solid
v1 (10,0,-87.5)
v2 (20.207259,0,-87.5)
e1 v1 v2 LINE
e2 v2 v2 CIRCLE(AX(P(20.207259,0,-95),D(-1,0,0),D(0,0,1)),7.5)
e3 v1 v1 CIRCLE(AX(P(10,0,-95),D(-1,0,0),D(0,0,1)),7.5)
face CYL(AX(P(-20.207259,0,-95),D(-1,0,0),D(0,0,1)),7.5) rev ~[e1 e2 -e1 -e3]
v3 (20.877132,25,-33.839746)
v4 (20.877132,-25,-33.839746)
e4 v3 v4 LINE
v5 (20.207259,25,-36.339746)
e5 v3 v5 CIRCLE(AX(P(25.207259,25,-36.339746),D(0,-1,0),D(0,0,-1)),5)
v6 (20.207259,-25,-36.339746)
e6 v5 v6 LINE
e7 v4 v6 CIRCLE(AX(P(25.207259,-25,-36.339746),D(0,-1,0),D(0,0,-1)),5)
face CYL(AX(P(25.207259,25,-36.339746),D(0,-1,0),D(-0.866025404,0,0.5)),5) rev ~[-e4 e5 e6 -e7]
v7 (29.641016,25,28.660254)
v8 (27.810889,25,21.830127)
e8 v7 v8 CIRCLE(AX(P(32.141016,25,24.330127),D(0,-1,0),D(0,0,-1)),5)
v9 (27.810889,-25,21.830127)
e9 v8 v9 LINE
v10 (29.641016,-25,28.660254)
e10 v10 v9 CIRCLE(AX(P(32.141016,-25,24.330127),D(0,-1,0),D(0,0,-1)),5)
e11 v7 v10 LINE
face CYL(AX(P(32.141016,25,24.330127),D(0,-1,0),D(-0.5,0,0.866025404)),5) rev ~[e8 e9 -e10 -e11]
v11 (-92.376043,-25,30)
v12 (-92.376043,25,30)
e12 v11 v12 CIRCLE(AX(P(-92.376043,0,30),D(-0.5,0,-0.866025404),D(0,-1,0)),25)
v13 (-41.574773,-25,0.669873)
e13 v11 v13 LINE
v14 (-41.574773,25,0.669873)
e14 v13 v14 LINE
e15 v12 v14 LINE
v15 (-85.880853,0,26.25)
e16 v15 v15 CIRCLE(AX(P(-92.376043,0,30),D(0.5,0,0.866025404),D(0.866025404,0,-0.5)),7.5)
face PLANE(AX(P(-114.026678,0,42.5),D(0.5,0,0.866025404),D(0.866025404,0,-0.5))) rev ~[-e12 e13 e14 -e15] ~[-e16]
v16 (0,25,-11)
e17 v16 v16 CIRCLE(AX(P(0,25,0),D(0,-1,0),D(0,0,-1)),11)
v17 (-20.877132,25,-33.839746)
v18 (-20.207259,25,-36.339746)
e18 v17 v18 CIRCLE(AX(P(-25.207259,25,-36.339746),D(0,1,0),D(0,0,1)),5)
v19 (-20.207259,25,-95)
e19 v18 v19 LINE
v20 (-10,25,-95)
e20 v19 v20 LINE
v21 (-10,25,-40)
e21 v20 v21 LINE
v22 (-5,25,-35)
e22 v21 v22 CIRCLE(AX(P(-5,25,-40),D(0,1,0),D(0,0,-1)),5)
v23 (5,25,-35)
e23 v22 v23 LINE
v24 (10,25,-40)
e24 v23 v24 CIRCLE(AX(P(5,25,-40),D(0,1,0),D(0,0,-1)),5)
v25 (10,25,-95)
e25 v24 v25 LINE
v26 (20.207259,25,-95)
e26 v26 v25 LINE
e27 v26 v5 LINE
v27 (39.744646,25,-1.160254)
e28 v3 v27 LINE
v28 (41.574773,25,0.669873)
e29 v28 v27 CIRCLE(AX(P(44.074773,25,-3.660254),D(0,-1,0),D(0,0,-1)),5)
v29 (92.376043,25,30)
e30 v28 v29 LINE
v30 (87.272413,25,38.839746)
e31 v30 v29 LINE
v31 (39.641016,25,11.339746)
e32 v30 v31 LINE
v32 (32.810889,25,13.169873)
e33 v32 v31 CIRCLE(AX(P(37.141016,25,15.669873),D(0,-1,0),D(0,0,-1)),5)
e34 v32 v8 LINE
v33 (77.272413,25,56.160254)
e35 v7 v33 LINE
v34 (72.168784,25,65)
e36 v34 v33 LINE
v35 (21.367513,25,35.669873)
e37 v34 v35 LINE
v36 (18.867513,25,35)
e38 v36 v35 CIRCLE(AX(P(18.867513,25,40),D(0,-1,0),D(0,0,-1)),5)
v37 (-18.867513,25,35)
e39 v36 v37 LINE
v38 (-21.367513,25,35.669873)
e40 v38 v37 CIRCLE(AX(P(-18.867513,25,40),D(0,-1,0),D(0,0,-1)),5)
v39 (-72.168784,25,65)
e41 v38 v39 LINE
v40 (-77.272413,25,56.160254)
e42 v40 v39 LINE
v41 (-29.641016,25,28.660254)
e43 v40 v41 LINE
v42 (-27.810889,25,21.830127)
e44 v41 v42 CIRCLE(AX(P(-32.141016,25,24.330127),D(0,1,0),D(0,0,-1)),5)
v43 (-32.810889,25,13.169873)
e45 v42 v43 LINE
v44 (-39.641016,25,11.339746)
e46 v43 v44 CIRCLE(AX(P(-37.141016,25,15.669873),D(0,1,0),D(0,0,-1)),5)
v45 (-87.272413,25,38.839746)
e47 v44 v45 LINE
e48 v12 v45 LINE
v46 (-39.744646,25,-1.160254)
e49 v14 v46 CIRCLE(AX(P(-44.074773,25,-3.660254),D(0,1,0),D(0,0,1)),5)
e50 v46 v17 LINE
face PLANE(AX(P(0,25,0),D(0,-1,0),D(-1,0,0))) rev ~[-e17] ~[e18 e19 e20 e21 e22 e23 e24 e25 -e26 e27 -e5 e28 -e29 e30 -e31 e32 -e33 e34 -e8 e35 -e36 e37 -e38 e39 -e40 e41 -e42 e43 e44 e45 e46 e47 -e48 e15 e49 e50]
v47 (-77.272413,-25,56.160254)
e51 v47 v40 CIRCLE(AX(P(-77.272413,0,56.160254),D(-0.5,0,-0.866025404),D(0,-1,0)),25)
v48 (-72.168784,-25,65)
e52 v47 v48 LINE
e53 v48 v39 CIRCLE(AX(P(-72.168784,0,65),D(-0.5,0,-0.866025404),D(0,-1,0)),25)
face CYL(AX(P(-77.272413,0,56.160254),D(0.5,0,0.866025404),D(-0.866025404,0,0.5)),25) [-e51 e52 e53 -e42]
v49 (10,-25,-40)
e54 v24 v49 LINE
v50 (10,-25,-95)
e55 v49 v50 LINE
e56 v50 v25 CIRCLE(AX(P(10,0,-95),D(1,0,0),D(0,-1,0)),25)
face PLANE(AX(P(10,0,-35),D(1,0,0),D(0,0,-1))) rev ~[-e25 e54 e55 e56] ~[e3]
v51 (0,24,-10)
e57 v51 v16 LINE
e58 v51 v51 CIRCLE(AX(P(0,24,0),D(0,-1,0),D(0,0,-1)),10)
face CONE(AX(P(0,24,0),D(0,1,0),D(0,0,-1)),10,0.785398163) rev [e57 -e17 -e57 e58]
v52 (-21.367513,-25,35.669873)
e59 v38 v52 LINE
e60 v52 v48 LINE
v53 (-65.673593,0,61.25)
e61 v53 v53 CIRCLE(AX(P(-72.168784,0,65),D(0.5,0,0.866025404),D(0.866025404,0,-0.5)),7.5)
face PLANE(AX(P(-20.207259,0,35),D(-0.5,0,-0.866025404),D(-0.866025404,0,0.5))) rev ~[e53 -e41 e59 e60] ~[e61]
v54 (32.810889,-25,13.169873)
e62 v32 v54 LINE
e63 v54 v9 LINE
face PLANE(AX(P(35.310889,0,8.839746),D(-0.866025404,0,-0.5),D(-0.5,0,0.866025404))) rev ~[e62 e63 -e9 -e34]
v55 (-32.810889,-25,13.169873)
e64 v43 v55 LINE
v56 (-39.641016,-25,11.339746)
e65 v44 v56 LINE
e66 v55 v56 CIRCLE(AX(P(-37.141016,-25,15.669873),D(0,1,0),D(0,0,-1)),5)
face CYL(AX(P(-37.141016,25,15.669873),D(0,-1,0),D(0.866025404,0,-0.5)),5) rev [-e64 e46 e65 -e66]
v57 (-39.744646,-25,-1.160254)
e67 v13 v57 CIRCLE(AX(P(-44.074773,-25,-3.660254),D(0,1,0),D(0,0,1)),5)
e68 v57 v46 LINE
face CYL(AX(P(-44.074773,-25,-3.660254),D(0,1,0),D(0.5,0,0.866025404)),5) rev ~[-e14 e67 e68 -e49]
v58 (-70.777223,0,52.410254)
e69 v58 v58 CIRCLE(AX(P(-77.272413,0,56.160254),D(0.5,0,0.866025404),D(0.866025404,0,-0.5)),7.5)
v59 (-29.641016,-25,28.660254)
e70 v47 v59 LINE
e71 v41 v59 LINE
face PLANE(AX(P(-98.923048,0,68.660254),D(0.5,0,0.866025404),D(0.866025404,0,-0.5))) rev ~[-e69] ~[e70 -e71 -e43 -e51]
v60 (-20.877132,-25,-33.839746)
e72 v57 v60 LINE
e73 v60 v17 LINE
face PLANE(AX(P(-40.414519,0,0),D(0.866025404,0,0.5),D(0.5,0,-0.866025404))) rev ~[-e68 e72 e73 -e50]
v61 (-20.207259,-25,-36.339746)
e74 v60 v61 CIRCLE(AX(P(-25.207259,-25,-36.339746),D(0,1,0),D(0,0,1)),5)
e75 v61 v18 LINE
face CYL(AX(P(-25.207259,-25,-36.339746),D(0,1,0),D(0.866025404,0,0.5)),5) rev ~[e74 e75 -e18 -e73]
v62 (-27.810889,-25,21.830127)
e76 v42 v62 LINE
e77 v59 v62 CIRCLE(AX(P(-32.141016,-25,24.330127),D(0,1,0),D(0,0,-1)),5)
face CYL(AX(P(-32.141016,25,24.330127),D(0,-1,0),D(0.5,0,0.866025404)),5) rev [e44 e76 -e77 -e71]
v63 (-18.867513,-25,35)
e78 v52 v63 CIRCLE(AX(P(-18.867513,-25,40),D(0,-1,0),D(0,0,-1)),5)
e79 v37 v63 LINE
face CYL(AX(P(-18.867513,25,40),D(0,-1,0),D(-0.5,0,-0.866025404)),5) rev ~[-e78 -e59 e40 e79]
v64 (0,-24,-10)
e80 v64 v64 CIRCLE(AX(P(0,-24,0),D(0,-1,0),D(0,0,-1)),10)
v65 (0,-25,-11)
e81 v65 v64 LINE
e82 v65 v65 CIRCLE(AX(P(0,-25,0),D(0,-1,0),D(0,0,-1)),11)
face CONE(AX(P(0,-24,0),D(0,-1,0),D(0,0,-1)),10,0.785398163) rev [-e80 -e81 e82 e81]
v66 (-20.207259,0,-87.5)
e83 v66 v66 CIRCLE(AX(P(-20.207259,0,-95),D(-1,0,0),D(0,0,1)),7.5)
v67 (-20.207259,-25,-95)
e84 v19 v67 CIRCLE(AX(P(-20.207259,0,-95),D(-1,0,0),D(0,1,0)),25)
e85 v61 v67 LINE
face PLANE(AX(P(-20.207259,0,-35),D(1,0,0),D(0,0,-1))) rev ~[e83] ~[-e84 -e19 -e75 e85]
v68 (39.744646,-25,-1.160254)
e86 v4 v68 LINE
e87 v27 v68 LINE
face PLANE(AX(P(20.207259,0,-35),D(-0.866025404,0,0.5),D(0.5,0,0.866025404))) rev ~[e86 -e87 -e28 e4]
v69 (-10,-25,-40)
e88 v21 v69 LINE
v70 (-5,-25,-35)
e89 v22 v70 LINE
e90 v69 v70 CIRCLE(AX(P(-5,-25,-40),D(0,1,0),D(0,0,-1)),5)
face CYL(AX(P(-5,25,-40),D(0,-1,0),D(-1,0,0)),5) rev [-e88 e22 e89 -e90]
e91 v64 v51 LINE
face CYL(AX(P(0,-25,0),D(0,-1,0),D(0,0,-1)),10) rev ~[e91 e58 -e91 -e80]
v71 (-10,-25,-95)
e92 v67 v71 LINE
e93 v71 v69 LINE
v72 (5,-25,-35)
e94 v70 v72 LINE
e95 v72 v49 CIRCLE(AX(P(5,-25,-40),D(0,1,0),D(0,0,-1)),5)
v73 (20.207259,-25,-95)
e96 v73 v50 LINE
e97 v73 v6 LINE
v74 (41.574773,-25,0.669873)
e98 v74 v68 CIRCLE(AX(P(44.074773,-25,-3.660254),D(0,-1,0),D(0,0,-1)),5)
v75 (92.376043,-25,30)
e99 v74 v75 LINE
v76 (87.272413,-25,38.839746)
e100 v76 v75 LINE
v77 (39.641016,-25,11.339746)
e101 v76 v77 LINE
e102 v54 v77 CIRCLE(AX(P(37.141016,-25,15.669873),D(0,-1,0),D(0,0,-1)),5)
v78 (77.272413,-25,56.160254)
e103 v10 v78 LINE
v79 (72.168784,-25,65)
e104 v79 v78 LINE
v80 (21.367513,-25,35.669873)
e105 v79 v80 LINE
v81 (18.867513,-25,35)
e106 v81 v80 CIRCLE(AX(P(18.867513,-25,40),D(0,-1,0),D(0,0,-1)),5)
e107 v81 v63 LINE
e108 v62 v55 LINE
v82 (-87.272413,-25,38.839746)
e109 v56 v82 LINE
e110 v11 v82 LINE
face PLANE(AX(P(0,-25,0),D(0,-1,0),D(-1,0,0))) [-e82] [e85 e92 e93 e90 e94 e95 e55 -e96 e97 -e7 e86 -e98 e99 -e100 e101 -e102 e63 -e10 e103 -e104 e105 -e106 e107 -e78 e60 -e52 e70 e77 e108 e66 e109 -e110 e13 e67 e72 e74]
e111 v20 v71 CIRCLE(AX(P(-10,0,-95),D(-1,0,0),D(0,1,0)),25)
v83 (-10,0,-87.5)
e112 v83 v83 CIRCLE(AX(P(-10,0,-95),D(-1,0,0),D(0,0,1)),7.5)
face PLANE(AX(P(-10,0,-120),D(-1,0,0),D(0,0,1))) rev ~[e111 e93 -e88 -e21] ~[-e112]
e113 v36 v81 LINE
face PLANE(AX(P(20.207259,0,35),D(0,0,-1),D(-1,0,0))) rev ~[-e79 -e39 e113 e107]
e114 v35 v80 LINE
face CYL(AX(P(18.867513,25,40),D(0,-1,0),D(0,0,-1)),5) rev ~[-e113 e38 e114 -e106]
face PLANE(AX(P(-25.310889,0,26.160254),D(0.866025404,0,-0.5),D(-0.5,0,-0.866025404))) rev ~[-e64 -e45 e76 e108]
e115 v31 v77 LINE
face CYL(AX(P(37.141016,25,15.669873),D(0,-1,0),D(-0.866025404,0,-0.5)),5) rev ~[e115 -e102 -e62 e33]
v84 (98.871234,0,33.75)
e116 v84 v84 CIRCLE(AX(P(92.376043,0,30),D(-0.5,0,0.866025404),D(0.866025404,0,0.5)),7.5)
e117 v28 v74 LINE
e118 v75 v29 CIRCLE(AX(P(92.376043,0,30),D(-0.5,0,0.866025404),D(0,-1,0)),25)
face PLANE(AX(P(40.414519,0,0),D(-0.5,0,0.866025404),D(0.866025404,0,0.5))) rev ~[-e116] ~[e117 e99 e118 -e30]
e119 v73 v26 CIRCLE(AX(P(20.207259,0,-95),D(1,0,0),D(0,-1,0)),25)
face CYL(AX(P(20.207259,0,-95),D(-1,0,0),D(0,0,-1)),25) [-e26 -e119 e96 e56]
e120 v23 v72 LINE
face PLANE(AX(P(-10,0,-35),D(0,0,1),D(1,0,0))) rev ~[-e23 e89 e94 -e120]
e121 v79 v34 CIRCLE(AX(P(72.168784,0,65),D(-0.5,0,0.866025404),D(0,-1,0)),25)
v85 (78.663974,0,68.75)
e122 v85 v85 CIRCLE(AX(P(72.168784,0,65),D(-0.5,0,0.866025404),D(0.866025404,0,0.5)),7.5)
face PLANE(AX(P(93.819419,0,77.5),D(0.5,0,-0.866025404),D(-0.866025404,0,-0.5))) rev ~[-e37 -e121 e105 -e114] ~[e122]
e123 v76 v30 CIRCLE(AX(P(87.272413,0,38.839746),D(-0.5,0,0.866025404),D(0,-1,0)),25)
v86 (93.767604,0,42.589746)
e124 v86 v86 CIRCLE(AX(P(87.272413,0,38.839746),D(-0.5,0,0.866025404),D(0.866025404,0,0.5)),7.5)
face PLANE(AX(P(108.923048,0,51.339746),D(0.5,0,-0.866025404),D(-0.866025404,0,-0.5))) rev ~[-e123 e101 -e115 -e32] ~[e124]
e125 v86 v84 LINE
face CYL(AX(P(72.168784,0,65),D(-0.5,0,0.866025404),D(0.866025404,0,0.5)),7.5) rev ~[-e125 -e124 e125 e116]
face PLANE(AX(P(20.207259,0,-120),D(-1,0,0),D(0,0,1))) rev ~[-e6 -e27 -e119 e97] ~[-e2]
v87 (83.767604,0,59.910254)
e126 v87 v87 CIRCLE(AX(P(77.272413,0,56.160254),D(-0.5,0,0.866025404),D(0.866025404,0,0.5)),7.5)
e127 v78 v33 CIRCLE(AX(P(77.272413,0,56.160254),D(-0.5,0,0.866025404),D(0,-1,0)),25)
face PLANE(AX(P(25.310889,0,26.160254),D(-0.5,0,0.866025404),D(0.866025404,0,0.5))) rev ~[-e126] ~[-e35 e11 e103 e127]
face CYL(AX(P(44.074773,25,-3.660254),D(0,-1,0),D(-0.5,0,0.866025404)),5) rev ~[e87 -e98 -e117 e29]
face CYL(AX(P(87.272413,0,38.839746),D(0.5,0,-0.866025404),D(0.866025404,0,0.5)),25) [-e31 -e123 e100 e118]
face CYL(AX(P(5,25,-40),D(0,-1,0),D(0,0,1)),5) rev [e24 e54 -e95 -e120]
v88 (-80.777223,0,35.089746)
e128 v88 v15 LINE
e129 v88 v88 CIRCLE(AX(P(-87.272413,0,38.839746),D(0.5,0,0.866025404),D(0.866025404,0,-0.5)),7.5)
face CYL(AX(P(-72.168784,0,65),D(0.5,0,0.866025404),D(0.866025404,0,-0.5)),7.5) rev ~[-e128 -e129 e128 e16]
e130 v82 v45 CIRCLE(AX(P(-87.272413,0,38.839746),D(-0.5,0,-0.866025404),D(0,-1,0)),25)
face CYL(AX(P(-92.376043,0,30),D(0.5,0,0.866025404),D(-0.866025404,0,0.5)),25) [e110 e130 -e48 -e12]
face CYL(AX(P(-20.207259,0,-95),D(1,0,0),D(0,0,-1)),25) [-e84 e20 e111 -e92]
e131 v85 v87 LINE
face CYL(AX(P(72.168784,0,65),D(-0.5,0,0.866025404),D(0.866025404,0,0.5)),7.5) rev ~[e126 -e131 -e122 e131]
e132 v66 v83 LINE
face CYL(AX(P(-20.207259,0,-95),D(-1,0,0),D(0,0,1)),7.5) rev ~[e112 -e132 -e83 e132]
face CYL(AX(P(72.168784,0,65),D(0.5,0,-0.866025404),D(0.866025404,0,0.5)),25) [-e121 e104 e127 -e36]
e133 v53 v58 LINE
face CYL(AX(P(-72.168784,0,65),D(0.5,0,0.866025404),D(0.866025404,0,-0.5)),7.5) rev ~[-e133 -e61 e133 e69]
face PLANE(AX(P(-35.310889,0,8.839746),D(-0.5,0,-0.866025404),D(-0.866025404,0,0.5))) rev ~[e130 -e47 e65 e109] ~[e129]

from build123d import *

# Parameters (mm, degrees)
THREE_ARM_BODY_50MM_DEPTH = 25
ARM_END_ROUND_B_RADIUS    = 25
ARM_END_ROUND_B_LENGTH    = 10.207259422
ARM_EDGE_FILLET_1_RADIUS  = 25
ARM_EDGE_FILLET_1_LENGTH  = 10.207259422
ARM_END_ROUND_A_RADIUS    = 25
ARM_END_ROUND_A_LENGTH    = 10.207259422
ARM_EDGE_FILLET_2_RADIUS  = 25
ARM_EDGE_FILLET_2_LENGTH  = 10.207259422
ARM_EDGE_FILLET_3_RADIUS  = 25
ARM_EDGE_FILLET_3_LENGTH  = 10.207259422
ARM_END_ROUND_C_RADIUS    = 25
ARM_END_ROUND_C_LENGTH    = 10.207259422
PIN_HOLE_A_15_REACH       = 188.921
PIN_HOLE_A_SKETCH_R       = 7.5
PIN_HOLE_B_15_REACH       = 188.921
PIN_HOLE_B_SKETCH_R       = 7.5
PIN_HOLE_C_15_REACH       = 183.779
PIN_HOLE_C_SKETCH_R       = 7.5
CENTER_BORE_SKETCH_R      = 10
CENTER_BORE_20_DEPTH      = 50
HUB_FILLET_R5_1_R         = 5
HUB_FILLET_R5_2_R         = 5
BORE_CHAMFER_1X45_SIZE    = 1


with BuildPart() as part:
    # Three-Arm Profile Sketch → Three-Arm Body 50mm (new, symmetric)
    with BuildSketch(Plane(origin=(0, 0, 0), x_dir=(1, 0, 0), z_dir=(0, 1, 0))):
        Polygon((-20.207259422, 35), (-20.207259422, 120), (-10, 120), (-10, 35), (10, 35), (10, 120), (20.207259422, 120), (20.207259422, 35), (40.414518843, 0), (114.026678165, -42.5), (108.923048454, -51.339745962), (35.310889132, -8.839745962), (25.310889132, -26.160254038), (98.923048454, -68.660254038), (93.819418743, -77.5), (20.207259422, -35), (-20.207259422, -35), (-93.819418743, -77.5), (-98.923048454, -68.660254038), (-25.310889132, -26.160254038), (-35.310889132, -8.839745962), (-108.923048454, -51.339745962), (-114.026678165, -42.5), (-40.414518843, 0), align=None)
    extrude(amount=THREE_ARM_BODY_50MM_DEPTH, both=True)

    # Arm End Round B: full round fillet: the end face becomes a half cylinder, R = half its width
    arm_end_round_b_face = Plane((-96.371233599, 0, 73.080127019), x_dir=(0.5, 0, 0.866025403784), z_dir=(-0.866025403784, 0, 0.5))  # on the end face: x along it, z out of the body
    arm_end_round_b_slab = arm_end_round_b_face.offset(-ARM_END_ROUND_B_RADIUS / 2) * Box(ARM_END_ROUND_B_LENGTH, 2 * ARM_END_ROUND_B_RADIUS, ARM_END_ROUND_B_RADIUS, mode=Mode.PRIVATE)  # the body's end, R deep
    arm_end_round_b_round = Plane((-74.720598504, 0, 60.580127019), x_dir=(-0.866025403784, 0, 0.5), z_dir=(0.5, 0, 0.866025403784)) * Cylinder(ARM_END_ROUND_B_RADIUS, ARM_END_ROUND_B_LENGTH, mode=Mode.PRIVATE)  # its axis R under the face
    add(arm_end_round_b_slab - arm_end_round_b_round, mode=Mode.SUBTRACT)

    # Arm Edge Fillet 1: full round fillet: the end face becomes a half cylinder, R = half its width
    arm_edge_fillet_1_face = Plane((-111.47486331, 0, 46.919872981), x_dir=(0.5, 0, 0.866025403784), z_dir=(-0.866025403784, 0, 0.5))  # on the end face: x along it, z out of the body
    arm_edge_fillet_1_slab = arm_edge_fillet_1_face.offset(-ARM_EDGE_FILLET_1_RADIUS / 2) * Box(ARM_EDGE_FILLET_1_LENGTH, 2 * ARM_EDGE_FILLET_1_RADIUS, ARM_EDGE_FILLET_1_RADIUS, mode=Mode.PRIVATE)  # the body's end, R deep
    arm_edge_fillet_1_round = Plane((-89.824228215, 0, 34.419872981), x_dir=(-0.866025403784, 0, 0.5), z_dir=(0.5, 0, 0.866025403784)) * Cylinder(ARM_EDGE_FILLET_1_RADIUS, ARM_EDGE_FILLET_1_LENGTH, mode=Mode.PRIVATE)  # its axis R under the face
    add(arm_edge_fillet_1_slab - arm_edge_fillet_1_round, mode=Mode.SUBTRACT)

    # Arm End Round A: full round fillet: the end face becomes a half cylinder, R = half its width
    arm_end_round_a_face = Plane((96.371233599, 0, 73.080127019), x_dir=(0.5, 0, -0.866025403784), z_dir=(0.866025403784, 0, 0.5))  # on the end face: x along it, z out of the body
    arm_end_round_a_slab = arm_end_round_a_face.offset(-ARM_END_ROUND_A_RADIUS / 2) * Box(ARM_END_ROUND_A_LENGTH, 2 * ARM_END_ROUND_A_RADIUS, ARM_END_ROUND_A_RADIUS, mode=Mode.PRIVATE)  # the body's end, R deep
    arm_end_round_a_round = Plane((74.720598504, 0, 60.580127019), x_dir=(0.866025403784, 0, 0.5), z_dir=(0.5, 0, -0.866025403784)) * Cylinder(ARM_END_ROUND_A_RADIUS, ARM_END_ROUND_A_LENGTH, mode=Mode.PRIVATE)  # its axis R under the face
    add(arm_end_round_a_slab - arm_end_round_a_round, mode=Mode.SUBTRACT)

    # Arm Edge Fillet 2: full round fillet: the end face becomes a half cylinder, R = half its width
    arm_edge_fillet_2_face = Plane((111.47486331, 0, 46.919872981), x_dir=(0.5, 0, -0.866025403784), z_dir=(0.866025403784, 0, 0.5))  # on the end face: x along it, z out of the body
    arm_edge_fillet_2_slab = arm_edge_fillet_2_face.offset(-ARM_EDGE_FILLET_2_RADIUS / 2) * Box(ARM_EDGE_FILLET_2_LENGTH, 2 * ARM_EDGE_FILLET_2_RADIUS, ARM_EDGE_FILLET_2_RADIUS, mode=Mode.PRIVATE)  # the body's end, R deep
    arm_edge_fillet_2_round = Plane((89.824228215, 0, 34.419872981), x_dir=(0.866025403784, 0, 0.5), z_dir=(0.5, 0, -0.866025403784)) * Cylinder(ARM_EDGE_FILLET_2_RADIUS, ARM_EDGE_FILLET_2_LENGTH, mode=Mode.PRIVATE)  # its axis R under the face
    add(arm_edge_fillet_2_slab - arm_edge_fillet_2_round, mode=Mode.SUBTRACT)

    # Arm Edge Fillet 3: full round fillet: the end face becomes a half cylinder, R = half its width
    arm_edge_fillet_3_face = Plane((15.103629711, 0, -120), x_dir=(-1, 0, 0), z_dir=(0, 0, -1))  # on the end face: x along it, z out of the body
    arm_edge_fillet_3_slab = arm_edge_fillet_3_face.offset(-ARM_EDGE_FILLET_3_RADIUS / 2) * Box(ARM_EDGE_FILLET_3_LENGTH, 2 * ARM_EDGE_FILLET_3_RADIUS, ARM_EDGE_FILLET_3_RADIUS, mode=Mode.PRIVATE)  # the body's end, R deep
    arm_edge_fillet_3_round = Plane((15.103629711, 0, -95), x_dir=(0, 0, -1), z_dir=(-1, 0, 0)) * Cylinder(ARM_EDGE_FILLET_3_RADIUS, ARM_EDGE_FILLET_3_LENGTH, mode=Mode.PRIVATE)  # its axis R under the face
    add(arm_edge_fillet_3_slab - arm_edge_fillet_3_round, mode=Mode.SUBTRACT)

    # Arm End Round C: full round fillet: the end face becomes a half cylinder, R = half its width
    arm_end_round_c_face = Plane((-15.103629711, 0, -120), x_dir=(1, 0, 0), z_dir=(0, 0, -1))  # on the end face: x along it, z out of the body
    arm_end_round_c_slab = arm_end_round_c_face.offset(-ARM_END_ROUND_C_RADIUS / 2) * Box(ARM_END_ROUND_C_LENGTH, 2 * ARM_END_ROUND_C_RADIUS, ARM_END_ROUND_C_RADIUS, mode=Mode.PRIVATE)  # the body's end, R deep
    arm_end_round_c_round = Plane((-15.103629711, 0, -95), x_dir=(0, 0, -1), z_dir=(1, 0, 0)) * Cylinder(ARM_END_ROUND_C_RADIUS, ARM_END_ROUND_C_LENGTH, mode=Mode.PRIVATE)  # its axis R under the face
    add(arm_end_round_c_slab - arm_end_round_c_round, mode=Mode.SUBTRACT)

    # Pin Hole A _15: up to this face of the body (flat: up to its plane)
    pin_hole_a_15_end = Plane(part.part.faces().sort_by_distance((75.066762447, 0, 20.006482173))[0])
    # Pin Hole A Sketch → Pin Hole A _15 (cut, up to the picked face)
    with BuildSketch(Plane(origin=(-10.103629711, 0, 17.5), x_dir=(0.8660254037844392, 0, 0.49999999999999917), z_dir=(-0.49999999999999917, 0, 0.8660254037844392)), mode=Mode.PRIVATE) as pin_hole_a_15_sk1:
        with Locations((95, 0)):
            Circle(PIN_HOLE_A_SKETCH_R)
    pin_hole_a_15_tool1 = split(extrude(pin_hole_a_15_sk1.sketch, amount=-PIN_HOLE_A_15_REACH, mode=Mode.PRIVATE), bisect_by=pin_hole_a_15_end, keep=Keep.BOTH, mode=Mode.PRIVATE)
    add(pin_hole_a_15_tool1.solids().sort_by(Axis((72.168784, 0, 65), (0.49999999999999917, 0, -0.8660254037844392)))[0], mode=Mode.SUBTRACT)

    # Pin Hole B _15: up to this face of the body (flat: up to its plane)
    pin_hole_b_15_end = Plane(part.part.faces().sort_by_distance((-75.066762447, 0, 20.006482173))[0])
    # Pin Hole B Sketch → Pin Hole B _15 (cut, up to the picked face)
    with BuildSketch(Plane(origin=(10.103629711, 0, 17.5), x_dir=(0.86602540378444, 0, -0.4999999999999976), z_dir=(0.4999999999999976, 0, 0.86602540378444)), mode=Mode.PRIVATE) as pin_hole_b_15_sk1:
        with Locations((-95, 0)):
            Circle(PIN_HOLE_B_SKETCH_R)
    pin_hole_b_15_tool1 = split(extrude(pin_hole_b_15_sk1.sketch, amount=-PIN_HOLE_B_15_REACH, mode=Mode.PRIVATE), bisect_by=pin_hole_b_15_end, keep=Keep.BOTH, mode=Mode.PRIVATE)
    add(pin_hole_b_15_tool1.solids().sort_by(Axis((-72.168784, 0, 65), (-0.4999999999999976, 0, -0.86602540378444)))[0], mode=Mode.SUBTRACT)

    # Pin Hole C _15: up to this face of the body (flat: up to its plane)
    pin_hole_c_15_end = Plane(part.part.faces().sort_by_distance((20.207259422, 0, -75.012964345))[0])
    # Pin Hole C Sketch → Pin Hole C _15 (cut, up to the picked face)
    with BuildSketch(Plane.ZY.offset(20.207259422), mode=Mode.PRIVATE) as pin_hole_c_15_sk1:
        with Locations((-95, 0)):
            Circle(PIN_HOLE_C_SKETCH_R)
    pin_hole_c_15_tool1 = split(extrude(pin_hole_c_15_sk1.sketch, amount=-PIN_HOLE_C_15_REACH, mode=Mode.PRIVATE), bisect_by=pin_hole_c_15_end, keep=Keep.BOTH, mode=Mode.PRIVATE)
    add(pin_hole_c_15_tool1.solids().sort_by(Axis((-20.207259, 0, -95), (1, 0, 0)))[0], mode=Mode.SUBTRACT)

    # Center Bore Sketch → Center Bore _20 (cut)
    with BuildSketch(Plane.XZ.offset(25)):
        with Locations(Location((0, 0, 0), (0, 0, 270))):
            Circle(CENTER_BORE_SKETCH_R)
    extrude(amount=-CENTER_BORE_20_DEPTH, mode=Mode.SUBTRACT)

    # Hub Fillet R5 1
    hub_fillet_r5_1_edges = [part.edges().sort_by_distance(p)[0] for p in [
        (35.310889132, 0, 8.839745962),
        (25.310889132, 0, 26.160254038),
        (-25.310889132, 0, 26.160254038),
        (-35.310889132, 0, 8.839745962),
        (-10, 0, -35),
        (10, 0, -35),
    ]]
    fillet(hub_fillet_r5_1_edges, radius=HUB_FILLET_R5_1_R)

    # Hub Fillet R5 2
    hub_fillet_r5_2_edges = [part.edges().sort_by_distance(p)[0] for p in [
        (20.207259422, 0, -35),
        (40.414518843, 0, 0),
        (20.207259422, 0, 35),
        (-20.207259422, 0, 35),
        (-40.414518843, 0, 0),
        (-20.207259422, 0, -35),
    ]]
    fillet(hub_fillet_r5_2_edges, radius=HUB_FILLET_R5_2_R)

    # Bore Chamfer 1x45
    bore_chamfer_1x45_edges = [part.edges().sort_by_distance(p)[0] for p in [
        (0, -25, 10),
        (0, 25, 10),
    ]]
    chamfer(bore_chamfer_1x45_edges, length=BORE_CHAMFER_1X45_SIZE)


solid = part.part
